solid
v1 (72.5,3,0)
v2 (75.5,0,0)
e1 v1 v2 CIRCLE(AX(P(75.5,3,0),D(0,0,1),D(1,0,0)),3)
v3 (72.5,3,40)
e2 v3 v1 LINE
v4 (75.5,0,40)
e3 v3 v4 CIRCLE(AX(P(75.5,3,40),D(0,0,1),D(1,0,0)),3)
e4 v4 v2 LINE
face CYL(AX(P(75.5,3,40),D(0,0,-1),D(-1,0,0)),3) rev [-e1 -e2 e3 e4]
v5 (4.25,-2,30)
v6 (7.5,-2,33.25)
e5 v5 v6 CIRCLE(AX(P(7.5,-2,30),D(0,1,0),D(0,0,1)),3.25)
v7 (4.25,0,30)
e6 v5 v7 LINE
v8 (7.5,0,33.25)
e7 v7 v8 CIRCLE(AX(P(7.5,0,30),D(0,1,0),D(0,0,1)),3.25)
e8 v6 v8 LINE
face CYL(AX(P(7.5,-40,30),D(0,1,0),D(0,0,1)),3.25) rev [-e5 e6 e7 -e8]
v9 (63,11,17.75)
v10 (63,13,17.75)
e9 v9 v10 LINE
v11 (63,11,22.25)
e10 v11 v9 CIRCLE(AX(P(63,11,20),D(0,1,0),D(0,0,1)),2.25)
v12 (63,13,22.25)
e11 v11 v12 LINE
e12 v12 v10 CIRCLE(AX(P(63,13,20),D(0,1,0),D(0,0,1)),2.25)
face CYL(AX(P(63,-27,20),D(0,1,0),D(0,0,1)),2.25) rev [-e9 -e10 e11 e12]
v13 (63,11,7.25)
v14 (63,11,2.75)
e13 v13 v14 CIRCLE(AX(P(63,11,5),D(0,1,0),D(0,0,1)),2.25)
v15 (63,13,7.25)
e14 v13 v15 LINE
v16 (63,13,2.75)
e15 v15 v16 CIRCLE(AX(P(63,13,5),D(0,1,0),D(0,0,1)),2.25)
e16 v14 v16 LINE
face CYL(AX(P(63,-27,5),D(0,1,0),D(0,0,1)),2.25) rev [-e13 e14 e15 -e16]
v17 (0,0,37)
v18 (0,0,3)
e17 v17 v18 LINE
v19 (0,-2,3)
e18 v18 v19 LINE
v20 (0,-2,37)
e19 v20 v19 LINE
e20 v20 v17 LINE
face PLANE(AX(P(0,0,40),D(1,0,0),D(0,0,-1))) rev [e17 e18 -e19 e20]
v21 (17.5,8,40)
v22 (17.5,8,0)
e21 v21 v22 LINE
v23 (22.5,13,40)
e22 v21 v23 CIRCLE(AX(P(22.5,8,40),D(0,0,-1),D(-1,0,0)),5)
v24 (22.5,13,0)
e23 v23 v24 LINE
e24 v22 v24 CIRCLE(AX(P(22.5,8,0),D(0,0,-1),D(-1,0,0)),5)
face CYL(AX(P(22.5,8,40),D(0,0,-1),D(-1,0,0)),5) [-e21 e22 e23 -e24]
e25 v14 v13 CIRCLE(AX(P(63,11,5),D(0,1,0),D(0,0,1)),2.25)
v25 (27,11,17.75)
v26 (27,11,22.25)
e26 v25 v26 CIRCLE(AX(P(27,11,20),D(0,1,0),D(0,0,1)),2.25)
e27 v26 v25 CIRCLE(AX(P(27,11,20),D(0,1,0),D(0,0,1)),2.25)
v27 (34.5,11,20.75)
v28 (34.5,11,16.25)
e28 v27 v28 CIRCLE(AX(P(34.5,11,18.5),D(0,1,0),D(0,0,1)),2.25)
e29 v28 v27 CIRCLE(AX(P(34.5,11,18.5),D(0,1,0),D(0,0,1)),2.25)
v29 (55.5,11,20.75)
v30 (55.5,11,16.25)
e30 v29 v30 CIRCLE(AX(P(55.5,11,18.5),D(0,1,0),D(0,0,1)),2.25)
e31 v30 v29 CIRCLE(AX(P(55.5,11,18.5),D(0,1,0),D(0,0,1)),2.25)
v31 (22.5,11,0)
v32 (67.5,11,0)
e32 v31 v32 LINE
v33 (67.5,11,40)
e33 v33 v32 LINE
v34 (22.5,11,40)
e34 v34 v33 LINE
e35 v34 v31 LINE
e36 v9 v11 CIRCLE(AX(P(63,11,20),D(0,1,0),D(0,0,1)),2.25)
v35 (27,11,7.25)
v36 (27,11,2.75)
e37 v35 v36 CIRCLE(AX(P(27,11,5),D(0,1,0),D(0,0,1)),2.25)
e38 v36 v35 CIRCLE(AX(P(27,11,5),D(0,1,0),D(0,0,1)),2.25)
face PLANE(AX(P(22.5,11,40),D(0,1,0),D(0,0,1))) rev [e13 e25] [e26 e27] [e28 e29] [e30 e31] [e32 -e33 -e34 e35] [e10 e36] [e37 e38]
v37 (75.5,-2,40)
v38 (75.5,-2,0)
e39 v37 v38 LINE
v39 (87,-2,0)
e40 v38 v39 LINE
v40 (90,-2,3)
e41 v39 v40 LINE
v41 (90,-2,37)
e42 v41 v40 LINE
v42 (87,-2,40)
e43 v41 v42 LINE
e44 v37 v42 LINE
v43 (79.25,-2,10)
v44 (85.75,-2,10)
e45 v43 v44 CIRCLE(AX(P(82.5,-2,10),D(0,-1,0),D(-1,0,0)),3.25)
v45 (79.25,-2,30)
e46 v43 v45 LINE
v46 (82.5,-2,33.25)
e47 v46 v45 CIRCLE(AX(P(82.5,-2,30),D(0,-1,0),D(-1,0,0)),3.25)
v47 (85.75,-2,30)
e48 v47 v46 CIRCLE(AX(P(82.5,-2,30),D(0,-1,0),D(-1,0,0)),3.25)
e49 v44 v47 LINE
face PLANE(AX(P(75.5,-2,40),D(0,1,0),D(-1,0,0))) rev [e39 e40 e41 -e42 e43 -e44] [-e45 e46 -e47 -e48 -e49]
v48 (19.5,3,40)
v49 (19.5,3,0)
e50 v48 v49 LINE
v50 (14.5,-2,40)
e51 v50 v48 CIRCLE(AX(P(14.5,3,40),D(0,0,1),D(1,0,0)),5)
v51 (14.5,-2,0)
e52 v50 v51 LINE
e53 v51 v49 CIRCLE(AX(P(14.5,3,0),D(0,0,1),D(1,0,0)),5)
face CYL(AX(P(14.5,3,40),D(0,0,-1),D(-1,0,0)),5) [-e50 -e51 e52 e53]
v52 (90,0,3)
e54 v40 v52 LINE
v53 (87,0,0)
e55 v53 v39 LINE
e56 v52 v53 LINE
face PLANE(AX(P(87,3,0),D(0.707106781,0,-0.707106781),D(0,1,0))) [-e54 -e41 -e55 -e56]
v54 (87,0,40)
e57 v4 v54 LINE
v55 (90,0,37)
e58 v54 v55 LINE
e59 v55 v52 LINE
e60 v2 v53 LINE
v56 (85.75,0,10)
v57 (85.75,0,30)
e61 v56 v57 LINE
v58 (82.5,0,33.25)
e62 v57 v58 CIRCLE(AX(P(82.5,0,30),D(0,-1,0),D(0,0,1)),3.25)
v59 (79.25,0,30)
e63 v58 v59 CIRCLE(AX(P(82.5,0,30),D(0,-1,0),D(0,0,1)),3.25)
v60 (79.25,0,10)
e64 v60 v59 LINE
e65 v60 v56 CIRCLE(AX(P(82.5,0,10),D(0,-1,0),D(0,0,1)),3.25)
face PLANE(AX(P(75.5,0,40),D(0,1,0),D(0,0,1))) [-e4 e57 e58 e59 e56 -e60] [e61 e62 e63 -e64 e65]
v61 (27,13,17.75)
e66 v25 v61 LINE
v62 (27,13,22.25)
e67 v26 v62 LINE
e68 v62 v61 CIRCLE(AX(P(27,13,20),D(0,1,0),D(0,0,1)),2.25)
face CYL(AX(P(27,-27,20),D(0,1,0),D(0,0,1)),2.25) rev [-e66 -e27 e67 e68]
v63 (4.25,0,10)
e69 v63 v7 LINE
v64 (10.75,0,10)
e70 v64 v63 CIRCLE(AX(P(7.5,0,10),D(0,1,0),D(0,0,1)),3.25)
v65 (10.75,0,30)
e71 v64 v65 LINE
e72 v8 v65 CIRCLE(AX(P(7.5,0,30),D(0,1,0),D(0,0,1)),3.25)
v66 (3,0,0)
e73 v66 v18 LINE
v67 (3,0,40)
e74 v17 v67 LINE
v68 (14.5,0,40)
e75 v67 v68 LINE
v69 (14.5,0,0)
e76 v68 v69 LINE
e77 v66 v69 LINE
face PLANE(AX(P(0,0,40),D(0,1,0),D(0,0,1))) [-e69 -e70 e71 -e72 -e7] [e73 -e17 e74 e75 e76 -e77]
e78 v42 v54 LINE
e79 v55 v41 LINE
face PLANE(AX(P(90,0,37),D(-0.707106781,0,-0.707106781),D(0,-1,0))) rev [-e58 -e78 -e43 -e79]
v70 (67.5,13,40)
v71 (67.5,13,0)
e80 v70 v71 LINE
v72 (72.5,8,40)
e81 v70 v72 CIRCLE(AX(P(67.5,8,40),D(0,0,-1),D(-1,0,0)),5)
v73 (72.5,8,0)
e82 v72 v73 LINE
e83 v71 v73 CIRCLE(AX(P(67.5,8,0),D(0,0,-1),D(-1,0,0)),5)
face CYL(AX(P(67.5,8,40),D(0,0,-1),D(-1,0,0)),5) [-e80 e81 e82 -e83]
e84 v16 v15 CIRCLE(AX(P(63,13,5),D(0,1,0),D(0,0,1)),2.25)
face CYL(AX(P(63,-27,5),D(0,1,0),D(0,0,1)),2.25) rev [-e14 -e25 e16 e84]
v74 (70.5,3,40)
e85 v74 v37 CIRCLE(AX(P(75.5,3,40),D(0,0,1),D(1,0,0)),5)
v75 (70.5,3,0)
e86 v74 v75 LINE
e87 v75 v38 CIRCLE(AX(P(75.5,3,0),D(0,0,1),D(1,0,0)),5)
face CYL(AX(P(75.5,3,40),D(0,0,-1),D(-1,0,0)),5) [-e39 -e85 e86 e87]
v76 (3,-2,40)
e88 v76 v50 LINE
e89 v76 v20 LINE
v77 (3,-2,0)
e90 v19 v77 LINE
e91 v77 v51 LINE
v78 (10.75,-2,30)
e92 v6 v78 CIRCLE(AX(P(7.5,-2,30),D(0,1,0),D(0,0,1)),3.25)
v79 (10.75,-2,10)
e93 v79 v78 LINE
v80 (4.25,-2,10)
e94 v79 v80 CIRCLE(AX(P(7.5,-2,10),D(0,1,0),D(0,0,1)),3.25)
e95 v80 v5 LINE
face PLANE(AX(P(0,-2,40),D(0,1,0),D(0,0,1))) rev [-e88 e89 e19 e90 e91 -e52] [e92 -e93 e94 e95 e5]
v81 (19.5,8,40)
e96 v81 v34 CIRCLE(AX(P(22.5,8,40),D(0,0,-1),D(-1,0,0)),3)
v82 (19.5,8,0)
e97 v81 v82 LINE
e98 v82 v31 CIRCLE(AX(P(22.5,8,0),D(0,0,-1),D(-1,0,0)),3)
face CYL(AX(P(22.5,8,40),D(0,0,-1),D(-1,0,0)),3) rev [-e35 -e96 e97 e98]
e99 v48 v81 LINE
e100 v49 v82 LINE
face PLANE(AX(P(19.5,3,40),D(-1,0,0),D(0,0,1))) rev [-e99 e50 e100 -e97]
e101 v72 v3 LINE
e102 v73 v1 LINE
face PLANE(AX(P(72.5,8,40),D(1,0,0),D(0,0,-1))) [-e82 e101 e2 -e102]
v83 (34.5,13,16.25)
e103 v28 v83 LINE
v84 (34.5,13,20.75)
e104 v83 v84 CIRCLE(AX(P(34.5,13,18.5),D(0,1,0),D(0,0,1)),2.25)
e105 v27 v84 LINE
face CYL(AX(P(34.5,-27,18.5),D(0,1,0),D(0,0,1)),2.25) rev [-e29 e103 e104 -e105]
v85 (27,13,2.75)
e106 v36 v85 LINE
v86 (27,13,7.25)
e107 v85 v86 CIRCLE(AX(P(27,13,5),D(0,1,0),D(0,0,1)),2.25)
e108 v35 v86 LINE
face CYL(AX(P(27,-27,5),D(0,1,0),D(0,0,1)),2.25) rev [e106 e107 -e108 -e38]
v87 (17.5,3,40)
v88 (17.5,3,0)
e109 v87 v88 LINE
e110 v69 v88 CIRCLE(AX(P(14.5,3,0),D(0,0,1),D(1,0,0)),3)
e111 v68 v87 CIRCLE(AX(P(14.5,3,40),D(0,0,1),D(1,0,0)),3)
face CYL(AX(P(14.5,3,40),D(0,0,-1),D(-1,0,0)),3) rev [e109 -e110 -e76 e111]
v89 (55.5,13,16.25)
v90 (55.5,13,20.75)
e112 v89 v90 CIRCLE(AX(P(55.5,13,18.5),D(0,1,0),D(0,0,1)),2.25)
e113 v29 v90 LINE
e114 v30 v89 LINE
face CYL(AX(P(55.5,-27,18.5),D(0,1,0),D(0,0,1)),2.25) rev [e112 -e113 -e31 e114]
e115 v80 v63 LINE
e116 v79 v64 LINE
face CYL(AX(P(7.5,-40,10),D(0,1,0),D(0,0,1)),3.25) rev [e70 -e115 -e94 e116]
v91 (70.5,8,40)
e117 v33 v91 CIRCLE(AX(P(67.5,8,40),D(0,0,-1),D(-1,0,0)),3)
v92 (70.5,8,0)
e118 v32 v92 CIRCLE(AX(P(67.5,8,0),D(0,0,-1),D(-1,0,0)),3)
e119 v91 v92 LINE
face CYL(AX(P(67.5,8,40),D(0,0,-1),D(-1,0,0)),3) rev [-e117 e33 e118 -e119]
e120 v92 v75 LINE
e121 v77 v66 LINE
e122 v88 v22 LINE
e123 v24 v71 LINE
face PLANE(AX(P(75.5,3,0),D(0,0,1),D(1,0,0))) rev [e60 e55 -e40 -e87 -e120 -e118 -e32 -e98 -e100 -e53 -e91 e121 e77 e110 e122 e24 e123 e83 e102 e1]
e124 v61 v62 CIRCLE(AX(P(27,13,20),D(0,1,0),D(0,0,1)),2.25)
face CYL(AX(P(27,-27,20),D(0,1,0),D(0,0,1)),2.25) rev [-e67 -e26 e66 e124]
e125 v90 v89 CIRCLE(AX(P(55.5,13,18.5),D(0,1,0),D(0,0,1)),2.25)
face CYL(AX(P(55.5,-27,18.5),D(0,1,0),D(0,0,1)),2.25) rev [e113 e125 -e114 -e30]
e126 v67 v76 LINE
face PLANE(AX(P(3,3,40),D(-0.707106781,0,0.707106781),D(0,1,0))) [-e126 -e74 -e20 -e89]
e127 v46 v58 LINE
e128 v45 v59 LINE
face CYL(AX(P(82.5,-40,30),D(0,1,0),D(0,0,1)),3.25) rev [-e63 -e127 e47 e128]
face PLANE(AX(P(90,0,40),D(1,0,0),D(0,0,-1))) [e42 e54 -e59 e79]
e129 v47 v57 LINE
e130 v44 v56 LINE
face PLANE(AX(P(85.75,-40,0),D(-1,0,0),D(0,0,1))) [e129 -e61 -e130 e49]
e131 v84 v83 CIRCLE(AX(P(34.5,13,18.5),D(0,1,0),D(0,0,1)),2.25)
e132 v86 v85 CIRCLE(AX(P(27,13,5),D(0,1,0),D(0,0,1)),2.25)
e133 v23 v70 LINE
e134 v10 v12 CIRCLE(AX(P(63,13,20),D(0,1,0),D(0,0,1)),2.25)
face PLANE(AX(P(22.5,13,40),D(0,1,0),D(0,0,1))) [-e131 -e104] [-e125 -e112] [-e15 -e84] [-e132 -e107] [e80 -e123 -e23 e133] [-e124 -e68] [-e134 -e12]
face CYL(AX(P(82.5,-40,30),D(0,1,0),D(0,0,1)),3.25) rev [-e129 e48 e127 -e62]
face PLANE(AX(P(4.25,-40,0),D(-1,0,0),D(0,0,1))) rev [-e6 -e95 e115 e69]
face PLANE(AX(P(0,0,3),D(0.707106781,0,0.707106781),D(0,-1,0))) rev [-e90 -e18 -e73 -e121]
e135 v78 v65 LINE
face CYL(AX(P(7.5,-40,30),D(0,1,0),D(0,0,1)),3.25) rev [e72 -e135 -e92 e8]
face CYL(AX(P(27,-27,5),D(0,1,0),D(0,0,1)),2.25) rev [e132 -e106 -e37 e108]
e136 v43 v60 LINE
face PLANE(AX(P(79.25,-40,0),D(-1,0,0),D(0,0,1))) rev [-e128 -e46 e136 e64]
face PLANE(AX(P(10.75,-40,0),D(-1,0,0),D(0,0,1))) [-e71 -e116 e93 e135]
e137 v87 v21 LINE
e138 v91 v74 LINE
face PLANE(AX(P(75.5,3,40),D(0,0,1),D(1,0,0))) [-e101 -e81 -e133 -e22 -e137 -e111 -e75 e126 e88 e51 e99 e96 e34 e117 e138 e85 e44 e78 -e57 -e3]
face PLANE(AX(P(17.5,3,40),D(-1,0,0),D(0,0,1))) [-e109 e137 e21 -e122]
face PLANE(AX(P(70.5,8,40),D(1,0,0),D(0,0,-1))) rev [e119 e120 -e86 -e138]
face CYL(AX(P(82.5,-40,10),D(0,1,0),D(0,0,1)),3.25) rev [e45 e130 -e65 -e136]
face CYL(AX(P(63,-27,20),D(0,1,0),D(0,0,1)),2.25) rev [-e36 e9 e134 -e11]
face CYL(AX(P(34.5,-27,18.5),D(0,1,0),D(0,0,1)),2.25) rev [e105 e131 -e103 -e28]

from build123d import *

# Parameters (mm, degrees)
EXTRUDE_1_DEPTH     = 40
CHAMFER_1_SIZE      = 3
CUT_EXTRUDE_1_DEPTH = 40
SKETCH_4_R          = 2.25
CUT_EXTRUDE_2_DEPTH = 40


with BuildPart() as part:
    # 草图2 → 凸台-拉伸1 (new body)
    with BuildSketch(Plane.XY):
        with BuildLine():
            Line((0, 0), (14.5, 0))
            ThreePointArc((14.5, 0), (16.621320344, 0.878679656), (17.5, 3))
            Line((17.5, 3), (17.5, 8))
            ThreePointArc((17.5, 8), (18.964466094, 11.535533906), (22.5, 13))
            Line((22.5, 13), (67.5, 13))
            ThreePointArc((67.5, 13), (71.035533906, 11.535533906), (72.5, 8))
            Line((72.5, 8), (72.5, 3))
            ThreePointArc((72.5, 3), (73.378679656, 0.878679656), (75.5, 0))
            Line((75.5, 0), (90, 0))
            Line((90, 0), (90, -2))
            Line((90, -2), (75.5, -2))
            ThreePointArc((75.5, -2), (71.964466094, -0.535533906), (70.5, 3))
            Line((70.5, 3), (70.5, 8))
            ThreePointArc((70.5, 8), (69.621320344, 10.121320344), (67.5, 11))
            Line((67.5, 11), (22.5, 11))
            ThreePointArc((22.5, 11), (20.378679656, 10.121320344), (19.5, 8))
            Line((19.5, 8), (19.5, 3))
            ThreePointArc((19.5, 3), (18.035533906, -0.535533906), (14.5, -2))
            Line((14.5, -2), (0, -2))
            Line((0, -2), (0, 0))
        make_face()
    extrude(amount=EXTRUDE_1_DEPTH)

    # 倒角1
    chamfer_1_edges = [part.edges().sort_by_distance(p)[0] for p in [
        (0, -1, 0),
        (90, -1, 0),
        (0, -1, 40),
        (90, -1, 40),
    ]]
    chamfer(chamfer_1_edges, length=CHAMFER_1_SIZE)

    # 草图3 → 切除-拉伸1 (cut)
    with BuildSketch(Plane(origin=(0, 0, 0), x_dir=(1, 0, 0), z_dir=(0, 1, 0))):
        with BuildLine():
            Line((4.25, -10), (4.25, -30))
            ThreePointArc((4.25, -30), (7.5, -33.25), (10.75, -30))
            Line((10.75, -30), (10.75, -10))
            ThreePointArc((10.75, -10), (7.5, -6.75), (4.25, -10))
        make_face()
        with BuildLine():
            ThreePointArc((85.75, -30), (82.5, -33.25), (79.25, -30))
            Line((79.25, -30), (79.25, -10))
            ThreePointArc((79.25, -10), (82.5, -6.75), (85.75, -10))
            Line((85.75, -10), (85.75, -30))
        make_face()
    extrude(amount=-CUT_EXTRUDE_1_DEPTH, mode=Mode.SUBTRACT)

    # 草图4 → 切除-拉伸2 (cut)
    with BuildSketch(Plane(origin=(0, 13, 0), x_dir=(1, 0, 0), z_dir=(0, 1, 0))):
        with Locations(Location((34.5, -18.5, 0), (0, 0, 270))):
            Circle(SKETCH_4_R)
        with Locations(Location((27, -20, 0), (0, 0, 270))):
            Circle(SKETCH_4_R)
        with Locations(Location((55.5, -18.5, 0), (0, 0, 270))):
            Circle(SKETCH_4_R)
        with Locations(Location((63, -20, 0), (0, 0, 270))):
            Circle(SKETCH_4_R)
        with Locations(Location((27, -5, 0), (0, 0, 270))):
            Circle(SKETCH_4_R)
        with Locations(Location((63, -5, 0), (0, 0, 270))):
            Circle(SKETCH_4_R)
    extrude(amount=-CUT_EXTRUDE_2_DEPTH, mode=Mode.SUBTRACT)


solid = part.part
